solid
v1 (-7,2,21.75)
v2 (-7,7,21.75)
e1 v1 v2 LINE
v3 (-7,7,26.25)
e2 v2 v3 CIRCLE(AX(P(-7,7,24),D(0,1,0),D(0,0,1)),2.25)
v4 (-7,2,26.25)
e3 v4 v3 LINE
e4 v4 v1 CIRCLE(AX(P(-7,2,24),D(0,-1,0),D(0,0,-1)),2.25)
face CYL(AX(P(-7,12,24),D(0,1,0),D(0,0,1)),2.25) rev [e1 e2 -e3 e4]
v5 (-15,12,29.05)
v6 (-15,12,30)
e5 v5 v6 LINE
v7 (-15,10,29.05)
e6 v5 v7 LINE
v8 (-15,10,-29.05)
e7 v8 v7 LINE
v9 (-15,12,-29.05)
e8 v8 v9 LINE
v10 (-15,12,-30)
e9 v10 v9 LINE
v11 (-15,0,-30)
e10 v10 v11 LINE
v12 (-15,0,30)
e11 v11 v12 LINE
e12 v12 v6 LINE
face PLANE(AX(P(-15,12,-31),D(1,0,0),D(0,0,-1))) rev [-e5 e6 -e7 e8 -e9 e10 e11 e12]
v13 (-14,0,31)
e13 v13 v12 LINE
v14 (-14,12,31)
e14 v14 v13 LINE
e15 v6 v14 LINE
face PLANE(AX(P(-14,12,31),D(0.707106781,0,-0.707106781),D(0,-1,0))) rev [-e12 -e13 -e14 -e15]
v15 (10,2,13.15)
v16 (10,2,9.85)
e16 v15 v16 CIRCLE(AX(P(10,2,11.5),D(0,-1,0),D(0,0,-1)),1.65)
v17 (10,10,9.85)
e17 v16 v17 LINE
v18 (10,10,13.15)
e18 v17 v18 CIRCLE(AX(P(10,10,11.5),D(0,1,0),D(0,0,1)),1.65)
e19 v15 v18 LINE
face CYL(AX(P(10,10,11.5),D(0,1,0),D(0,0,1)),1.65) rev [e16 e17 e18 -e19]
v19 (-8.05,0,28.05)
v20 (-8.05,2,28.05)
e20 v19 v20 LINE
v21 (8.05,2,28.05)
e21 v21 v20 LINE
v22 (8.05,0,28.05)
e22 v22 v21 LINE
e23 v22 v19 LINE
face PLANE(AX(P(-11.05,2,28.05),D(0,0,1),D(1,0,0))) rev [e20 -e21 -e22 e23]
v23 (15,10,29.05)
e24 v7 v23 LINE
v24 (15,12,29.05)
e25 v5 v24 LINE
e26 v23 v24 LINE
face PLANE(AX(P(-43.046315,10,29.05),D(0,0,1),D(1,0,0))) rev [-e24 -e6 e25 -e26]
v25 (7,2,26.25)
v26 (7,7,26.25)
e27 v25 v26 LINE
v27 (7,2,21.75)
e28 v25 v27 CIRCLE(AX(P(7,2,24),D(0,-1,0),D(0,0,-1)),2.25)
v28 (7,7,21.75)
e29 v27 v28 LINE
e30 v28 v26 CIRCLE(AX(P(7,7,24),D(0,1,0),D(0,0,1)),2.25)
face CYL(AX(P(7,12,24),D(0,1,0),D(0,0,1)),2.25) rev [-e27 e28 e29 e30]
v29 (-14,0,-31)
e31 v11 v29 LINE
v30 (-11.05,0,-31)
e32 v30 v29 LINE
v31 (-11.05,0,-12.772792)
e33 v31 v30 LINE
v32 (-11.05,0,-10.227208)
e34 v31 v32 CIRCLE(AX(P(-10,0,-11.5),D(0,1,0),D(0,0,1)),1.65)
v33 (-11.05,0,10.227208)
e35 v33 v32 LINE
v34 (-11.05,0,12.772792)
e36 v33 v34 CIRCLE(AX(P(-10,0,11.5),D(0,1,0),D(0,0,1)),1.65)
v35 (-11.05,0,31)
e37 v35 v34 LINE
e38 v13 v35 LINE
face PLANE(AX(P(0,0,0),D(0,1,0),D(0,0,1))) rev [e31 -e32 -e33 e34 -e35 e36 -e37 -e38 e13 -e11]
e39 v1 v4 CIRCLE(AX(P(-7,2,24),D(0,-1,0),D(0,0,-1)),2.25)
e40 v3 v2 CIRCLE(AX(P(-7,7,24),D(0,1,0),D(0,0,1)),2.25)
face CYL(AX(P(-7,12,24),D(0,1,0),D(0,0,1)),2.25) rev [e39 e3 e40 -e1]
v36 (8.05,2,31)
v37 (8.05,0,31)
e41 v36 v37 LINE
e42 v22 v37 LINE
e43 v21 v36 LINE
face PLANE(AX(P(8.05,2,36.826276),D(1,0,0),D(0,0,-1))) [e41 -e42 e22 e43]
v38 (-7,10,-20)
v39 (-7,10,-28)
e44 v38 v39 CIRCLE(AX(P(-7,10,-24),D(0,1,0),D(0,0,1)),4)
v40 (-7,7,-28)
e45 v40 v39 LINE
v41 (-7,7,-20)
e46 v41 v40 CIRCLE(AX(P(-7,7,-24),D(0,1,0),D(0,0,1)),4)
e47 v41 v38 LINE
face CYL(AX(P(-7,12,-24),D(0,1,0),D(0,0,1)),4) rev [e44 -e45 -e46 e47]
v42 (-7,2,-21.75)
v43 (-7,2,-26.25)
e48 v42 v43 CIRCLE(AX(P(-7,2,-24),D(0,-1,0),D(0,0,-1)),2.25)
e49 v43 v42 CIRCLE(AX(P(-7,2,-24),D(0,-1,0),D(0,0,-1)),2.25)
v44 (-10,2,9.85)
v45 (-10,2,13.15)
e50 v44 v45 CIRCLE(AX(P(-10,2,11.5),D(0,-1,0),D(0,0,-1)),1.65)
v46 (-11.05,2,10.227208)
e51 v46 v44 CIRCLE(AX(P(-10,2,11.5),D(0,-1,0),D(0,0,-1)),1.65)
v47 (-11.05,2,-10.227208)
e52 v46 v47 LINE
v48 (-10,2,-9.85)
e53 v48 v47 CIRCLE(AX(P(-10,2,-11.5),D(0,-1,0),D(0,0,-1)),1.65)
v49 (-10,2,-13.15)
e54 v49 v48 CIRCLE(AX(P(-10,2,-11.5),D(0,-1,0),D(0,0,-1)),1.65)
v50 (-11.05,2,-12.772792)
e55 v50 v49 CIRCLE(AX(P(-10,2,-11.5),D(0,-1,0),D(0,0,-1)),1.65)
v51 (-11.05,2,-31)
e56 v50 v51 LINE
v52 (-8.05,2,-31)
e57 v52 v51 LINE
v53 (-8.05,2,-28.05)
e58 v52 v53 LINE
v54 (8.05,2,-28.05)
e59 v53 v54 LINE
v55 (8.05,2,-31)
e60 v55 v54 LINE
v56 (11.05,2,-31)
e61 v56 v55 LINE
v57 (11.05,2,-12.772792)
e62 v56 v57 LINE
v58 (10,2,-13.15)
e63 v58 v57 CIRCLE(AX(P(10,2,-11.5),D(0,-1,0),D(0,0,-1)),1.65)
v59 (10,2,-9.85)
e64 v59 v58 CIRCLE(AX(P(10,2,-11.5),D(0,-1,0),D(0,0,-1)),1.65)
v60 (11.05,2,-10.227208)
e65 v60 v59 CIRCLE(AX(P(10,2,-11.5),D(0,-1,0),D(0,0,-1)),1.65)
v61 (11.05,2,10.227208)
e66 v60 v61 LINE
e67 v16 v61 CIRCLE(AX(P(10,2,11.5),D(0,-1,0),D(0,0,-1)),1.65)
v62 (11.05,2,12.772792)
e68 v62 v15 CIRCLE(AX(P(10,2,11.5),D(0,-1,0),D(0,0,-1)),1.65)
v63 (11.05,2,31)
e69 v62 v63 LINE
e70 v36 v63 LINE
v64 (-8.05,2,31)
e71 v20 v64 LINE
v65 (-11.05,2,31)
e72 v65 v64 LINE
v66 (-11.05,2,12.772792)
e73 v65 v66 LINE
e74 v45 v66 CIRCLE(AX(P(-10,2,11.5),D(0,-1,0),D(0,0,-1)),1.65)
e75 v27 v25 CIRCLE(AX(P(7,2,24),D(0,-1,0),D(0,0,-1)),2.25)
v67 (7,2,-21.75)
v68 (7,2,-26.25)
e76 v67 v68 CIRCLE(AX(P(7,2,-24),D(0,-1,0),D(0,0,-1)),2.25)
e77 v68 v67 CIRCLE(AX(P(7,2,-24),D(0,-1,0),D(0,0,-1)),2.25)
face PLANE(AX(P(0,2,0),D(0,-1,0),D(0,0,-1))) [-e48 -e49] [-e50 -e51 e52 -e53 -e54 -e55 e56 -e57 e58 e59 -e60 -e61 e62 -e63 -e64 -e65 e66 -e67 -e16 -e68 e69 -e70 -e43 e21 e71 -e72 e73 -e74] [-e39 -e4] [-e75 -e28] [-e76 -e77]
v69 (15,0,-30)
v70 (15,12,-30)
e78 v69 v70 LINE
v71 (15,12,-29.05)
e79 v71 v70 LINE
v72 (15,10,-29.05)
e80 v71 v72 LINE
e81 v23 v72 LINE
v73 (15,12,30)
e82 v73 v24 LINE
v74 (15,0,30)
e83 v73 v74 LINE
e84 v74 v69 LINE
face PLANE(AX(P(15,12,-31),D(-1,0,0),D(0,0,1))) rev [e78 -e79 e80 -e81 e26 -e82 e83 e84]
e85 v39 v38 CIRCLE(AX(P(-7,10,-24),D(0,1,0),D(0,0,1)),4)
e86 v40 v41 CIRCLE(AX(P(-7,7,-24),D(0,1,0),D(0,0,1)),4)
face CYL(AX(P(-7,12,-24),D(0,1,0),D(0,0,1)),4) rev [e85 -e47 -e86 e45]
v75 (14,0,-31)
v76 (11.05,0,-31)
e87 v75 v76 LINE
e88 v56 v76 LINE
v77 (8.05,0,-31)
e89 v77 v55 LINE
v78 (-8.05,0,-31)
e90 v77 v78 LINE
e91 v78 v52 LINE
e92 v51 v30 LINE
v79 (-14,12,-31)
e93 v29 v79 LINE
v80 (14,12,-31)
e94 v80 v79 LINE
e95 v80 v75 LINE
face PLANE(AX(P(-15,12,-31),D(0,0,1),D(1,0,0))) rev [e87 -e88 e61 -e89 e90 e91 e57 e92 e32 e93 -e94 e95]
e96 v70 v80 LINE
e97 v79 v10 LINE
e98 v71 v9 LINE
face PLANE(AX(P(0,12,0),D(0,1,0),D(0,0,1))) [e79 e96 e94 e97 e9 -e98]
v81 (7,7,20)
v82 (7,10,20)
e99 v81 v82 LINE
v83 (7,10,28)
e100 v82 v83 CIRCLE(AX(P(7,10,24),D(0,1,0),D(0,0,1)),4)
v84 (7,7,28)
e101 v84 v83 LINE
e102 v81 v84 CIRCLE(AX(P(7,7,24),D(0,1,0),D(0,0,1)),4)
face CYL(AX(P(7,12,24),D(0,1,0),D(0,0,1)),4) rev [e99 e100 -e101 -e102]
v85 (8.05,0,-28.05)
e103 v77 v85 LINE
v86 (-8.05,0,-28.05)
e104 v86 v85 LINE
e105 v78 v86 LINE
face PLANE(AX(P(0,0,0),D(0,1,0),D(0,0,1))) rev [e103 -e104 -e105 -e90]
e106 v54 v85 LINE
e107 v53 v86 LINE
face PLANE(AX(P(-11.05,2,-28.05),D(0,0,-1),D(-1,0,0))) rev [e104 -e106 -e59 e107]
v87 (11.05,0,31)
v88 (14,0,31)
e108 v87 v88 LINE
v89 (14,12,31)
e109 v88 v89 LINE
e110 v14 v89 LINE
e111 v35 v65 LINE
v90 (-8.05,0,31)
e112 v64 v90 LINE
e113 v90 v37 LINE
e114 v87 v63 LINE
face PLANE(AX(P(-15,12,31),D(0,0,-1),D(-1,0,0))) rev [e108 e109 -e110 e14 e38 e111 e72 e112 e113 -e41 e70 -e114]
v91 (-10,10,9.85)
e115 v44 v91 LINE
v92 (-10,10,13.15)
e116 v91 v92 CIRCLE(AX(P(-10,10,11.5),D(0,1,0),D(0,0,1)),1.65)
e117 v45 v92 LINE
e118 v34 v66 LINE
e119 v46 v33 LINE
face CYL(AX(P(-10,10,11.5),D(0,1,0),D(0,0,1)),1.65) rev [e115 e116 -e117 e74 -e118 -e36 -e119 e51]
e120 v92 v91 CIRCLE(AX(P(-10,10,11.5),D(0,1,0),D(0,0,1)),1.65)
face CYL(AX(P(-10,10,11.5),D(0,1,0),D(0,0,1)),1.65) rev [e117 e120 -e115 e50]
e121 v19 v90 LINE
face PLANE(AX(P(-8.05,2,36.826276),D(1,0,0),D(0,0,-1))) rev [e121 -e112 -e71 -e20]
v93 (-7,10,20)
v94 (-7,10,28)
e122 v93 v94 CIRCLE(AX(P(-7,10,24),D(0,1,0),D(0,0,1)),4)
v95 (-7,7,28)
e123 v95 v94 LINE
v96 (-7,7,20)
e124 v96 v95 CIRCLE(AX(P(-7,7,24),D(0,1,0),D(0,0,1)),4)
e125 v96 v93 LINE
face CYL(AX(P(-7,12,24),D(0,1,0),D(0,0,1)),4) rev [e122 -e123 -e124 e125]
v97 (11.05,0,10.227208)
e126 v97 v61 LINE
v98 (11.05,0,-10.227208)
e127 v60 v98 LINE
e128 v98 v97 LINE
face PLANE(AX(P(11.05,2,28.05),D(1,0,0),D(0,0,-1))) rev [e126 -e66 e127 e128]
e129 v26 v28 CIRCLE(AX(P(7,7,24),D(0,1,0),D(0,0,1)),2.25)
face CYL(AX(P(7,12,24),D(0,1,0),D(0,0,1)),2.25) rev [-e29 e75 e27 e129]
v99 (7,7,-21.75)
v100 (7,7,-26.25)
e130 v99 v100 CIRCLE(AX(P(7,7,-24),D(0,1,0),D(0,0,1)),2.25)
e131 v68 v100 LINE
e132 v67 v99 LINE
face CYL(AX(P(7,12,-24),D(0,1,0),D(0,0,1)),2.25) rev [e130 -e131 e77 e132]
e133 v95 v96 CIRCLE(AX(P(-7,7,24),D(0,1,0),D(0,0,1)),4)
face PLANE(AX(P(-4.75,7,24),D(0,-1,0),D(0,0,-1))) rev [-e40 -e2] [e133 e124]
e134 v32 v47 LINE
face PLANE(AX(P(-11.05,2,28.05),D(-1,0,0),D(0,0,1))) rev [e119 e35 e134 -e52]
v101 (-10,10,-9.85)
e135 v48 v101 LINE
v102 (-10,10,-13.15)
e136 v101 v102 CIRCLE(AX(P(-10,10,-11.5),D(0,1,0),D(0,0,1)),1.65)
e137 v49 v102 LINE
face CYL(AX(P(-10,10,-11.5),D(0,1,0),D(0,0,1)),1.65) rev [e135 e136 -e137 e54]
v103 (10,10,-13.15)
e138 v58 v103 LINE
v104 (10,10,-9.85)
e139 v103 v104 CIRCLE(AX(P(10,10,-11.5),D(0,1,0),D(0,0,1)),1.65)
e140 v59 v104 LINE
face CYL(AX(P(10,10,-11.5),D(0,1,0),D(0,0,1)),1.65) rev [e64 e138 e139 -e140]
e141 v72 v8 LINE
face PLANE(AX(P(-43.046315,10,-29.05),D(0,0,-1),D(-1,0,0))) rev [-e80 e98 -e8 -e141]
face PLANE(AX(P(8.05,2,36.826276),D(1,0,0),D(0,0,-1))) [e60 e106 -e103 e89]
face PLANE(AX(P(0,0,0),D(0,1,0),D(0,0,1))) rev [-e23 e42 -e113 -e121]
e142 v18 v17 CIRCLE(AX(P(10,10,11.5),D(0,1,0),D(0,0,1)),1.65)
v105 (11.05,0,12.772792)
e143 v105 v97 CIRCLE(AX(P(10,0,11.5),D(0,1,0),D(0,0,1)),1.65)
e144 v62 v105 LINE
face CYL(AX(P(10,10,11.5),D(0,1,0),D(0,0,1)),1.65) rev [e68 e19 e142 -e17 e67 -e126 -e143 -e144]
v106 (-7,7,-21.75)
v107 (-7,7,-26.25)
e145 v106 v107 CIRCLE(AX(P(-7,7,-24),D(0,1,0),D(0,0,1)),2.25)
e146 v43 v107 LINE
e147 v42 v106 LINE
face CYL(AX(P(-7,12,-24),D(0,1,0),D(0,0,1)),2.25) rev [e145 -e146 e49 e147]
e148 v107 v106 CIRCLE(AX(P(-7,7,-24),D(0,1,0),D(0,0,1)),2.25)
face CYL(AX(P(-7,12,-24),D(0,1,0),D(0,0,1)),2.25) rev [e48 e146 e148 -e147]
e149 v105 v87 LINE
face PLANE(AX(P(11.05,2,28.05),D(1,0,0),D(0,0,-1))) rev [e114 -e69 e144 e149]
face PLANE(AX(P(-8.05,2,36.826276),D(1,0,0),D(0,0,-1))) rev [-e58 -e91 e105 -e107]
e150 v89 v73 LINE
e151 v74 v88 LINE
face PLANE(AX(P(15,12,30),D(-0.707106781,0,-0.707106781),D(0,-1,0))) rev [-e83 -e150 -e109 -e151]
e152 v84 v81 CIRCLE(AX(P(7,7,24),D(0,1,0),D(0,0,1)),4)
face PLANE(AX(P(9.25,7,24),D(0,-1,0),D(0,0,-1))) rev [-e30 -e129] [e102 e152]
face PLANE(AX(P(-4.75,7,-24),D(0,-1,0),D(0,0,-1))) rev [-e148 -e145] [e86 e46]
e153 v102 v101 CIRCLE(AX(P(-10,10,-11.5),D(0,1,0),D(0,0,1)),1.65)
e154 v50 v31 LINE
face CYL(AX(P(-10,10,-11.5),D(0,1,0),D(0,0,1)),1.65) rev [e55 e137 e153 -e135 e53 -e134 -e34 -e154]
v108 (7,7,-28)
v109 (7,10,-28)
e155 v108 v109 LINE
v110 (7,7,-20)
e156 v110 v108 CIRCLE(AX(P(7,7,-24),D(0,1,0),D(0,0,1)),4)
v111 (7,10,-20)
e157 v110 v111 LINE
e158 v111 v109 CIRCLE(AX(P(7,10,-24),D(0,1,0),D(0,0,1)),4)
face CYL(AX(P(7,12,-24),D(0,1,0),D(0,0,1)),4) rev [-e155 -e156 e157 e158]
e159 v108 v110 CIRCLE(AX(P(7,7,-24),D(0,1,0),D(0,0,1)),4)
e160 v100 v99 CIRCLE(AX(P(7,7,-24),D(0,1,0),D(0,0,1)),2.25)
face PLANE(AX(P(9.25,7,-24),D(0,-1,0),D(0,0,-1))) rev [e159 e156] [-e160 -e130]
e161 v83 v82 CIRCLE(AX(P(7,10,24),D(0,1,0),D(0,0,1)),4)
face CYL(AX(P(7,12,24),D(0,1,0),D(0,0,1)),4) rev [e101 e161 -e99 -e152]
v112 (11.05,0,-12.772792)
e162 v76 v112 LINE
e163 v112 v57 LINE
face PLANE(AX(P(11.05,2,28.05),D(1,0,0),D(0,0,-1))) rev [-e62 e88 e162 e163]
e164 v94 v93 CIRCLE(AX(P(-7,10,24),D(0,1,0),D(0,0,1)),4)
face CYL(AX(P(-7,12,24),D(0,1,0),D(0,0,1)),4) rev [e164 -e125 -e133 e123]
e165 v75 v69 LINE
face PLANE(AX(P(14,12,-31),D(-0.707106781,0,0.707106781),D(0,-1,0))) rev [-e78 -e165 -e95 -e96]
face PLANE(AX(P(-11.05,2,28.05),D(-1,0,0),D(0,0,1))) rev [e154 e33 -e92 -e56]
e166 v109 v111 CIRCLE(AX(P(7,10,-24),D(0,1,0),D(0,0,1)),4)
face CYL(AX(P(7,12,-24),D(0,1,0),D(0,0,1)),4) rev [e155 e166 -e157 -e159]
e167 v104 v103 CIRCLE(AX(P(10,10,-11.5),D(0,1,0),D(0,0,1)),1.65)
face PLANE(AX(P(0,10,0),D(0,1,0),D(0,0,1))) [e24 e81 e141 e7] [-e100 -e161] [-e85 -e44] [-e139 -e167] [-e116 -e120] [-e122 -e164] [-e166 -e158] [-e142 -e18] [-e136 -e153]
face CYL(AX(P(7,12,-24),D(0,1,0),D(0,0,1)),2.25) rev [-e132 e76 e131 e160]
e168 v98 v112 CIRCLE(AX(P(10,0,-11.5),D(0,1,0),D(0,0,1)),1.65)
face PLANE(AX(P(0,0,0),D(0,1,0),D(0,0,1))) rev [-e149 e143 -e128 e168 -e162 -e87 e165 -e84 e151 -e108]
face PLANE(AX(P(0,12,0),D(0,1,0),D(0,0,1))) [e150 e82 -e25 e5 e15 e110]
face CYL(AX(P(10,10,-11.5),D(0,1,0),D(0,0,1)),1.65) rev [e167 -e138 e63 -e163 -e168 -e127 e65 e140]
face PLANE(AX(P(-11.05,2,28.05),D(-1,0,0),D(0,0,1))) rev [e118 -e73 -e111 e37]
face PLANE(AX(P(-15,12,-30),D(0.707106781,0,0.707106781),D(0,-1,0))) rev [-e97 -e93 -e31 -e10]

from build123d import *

# Parameters (mm, degrees)
SKETCH_1_W                = 30
SKETCH_1_H                = 62
EXTRUDE_1_DEPTH           = 12
SKETCH_2_W                = 22.1
SKETCH_2_H                = 56.1
CUT_EXTRUDE_1_DEPTH       = 2
SKETCH_3_W                = 3
SKETCH_3_H                = 72.139143417
CUT_EXTRUDE_2_DEPTH       = 2
SKETCH_4_W                = 86.092630608
SKETCH_4_H                = 58.1
CUT_EXTRUDE_3_DEPTH       = 2
HOLE_WIZARD_M4_1_D        = 3.3
HOLE_WIZARD_1_D           = 4.5
HOLE_WIZARD_1_CBORE_D     = 8
HOLE_WIZARD_1_CBORE_DEPTH = 5
CHAMFER_1_SIZE            = 1


with BuildPart() as part:
    # 草图1 → 凸台-拉伸1 (new body)
    with BuildSketch(Plane(origin=(0, 0, 0), x_dir=(1, 0, 0), z_dir=(0, 1, 0))):
        Rectangle(SKETCH_1_W, SKETCH_1_H)
    extrude(amount=EXTRUDE_1_DEPTH)

    # 草图2 → 切除-拉伸1 (cut)
    with BuildSketch(Plane.XZ):
        Rectangle(SKETCH_2_W, SKETCH_2_H)
    extrude(amount=-CUT_EXTRUDE_1_DEPTH, mode=Mode.SUBTRACT)

    # 草图3 → 切除-拉伸2 (cut)
    with BuildSketch(Plane.XZ):
        with Locations((-9.55, 0.756704302)):
            Rectangle(SKETCH_3_W, SKETCH_3_H)
    cut_extrude_2 = extrude(amount=-CUT_EXTRUDE_2_DEPTH, mode=Mode.SUBTRACT)

    # 镜向1: 切除-拉伸2 across plane
    add(cut_extrude_2.mirror(Plane(origin=(0, 0, 0), x_dir=(0, 0, 1), z_dir=(1, 0, 0))), mode=Mode.SUBTRACT)

    # 草图4 → 切除-拉伸3 (cut)
    with BuildSketch(Plane(origin=(0, 12, 0), x_dir=(1, 0, 0), z_dir=(0, 1, 0))):
        Rectangle(SKETCH_4_W, SKETCH_4_H)
    extrude(amount=-CUT_EXTRUDE_3_DEPTH, mode=Mode.SUBTRACT)

    # M4 螺纹孔1 (through all)
    with Locations(Plane(origin=(0, 10, 0), x_dir=(1, 0, 0), z_dir=(0, 1, 0))):
        with Locations((-10, 11.5), (10, 11.5), (-10, -11.5), (10, -11.5)):
            Hole(HOLE_WIZARD_M4_1_D / 2)

    # 打孔尺寸(%根据)开槽圆柱头螺钉的类型1 (through all)
    with Locations(Plane(origin=(0, 12, 0), x_dir=(1, 0, 0), z_dir=(0, 1, 0))):
        with Locations((-7, 24), (7, 24), (-7, -24), (7, -24)):
            CounterBoreHole(HOLE_WIZARD_1_D / 2, HOLE_WIZARD_1_CBORE_D / 2, HOLE_WIZARD_1_CBORE_DEPTH)

    # 倒角1
    chamfer_1_edges = [part.edges().sort_by_distance(p)[0] for p in [
        (15, 6, 31),
        (-15, 6, 31),
        (-15, 6, -31),
        (15, 6, -31),
    ]]
    chamfer(chamfer_1_edges, length=CHAMFER_1_SIZE)


solid = part.part
